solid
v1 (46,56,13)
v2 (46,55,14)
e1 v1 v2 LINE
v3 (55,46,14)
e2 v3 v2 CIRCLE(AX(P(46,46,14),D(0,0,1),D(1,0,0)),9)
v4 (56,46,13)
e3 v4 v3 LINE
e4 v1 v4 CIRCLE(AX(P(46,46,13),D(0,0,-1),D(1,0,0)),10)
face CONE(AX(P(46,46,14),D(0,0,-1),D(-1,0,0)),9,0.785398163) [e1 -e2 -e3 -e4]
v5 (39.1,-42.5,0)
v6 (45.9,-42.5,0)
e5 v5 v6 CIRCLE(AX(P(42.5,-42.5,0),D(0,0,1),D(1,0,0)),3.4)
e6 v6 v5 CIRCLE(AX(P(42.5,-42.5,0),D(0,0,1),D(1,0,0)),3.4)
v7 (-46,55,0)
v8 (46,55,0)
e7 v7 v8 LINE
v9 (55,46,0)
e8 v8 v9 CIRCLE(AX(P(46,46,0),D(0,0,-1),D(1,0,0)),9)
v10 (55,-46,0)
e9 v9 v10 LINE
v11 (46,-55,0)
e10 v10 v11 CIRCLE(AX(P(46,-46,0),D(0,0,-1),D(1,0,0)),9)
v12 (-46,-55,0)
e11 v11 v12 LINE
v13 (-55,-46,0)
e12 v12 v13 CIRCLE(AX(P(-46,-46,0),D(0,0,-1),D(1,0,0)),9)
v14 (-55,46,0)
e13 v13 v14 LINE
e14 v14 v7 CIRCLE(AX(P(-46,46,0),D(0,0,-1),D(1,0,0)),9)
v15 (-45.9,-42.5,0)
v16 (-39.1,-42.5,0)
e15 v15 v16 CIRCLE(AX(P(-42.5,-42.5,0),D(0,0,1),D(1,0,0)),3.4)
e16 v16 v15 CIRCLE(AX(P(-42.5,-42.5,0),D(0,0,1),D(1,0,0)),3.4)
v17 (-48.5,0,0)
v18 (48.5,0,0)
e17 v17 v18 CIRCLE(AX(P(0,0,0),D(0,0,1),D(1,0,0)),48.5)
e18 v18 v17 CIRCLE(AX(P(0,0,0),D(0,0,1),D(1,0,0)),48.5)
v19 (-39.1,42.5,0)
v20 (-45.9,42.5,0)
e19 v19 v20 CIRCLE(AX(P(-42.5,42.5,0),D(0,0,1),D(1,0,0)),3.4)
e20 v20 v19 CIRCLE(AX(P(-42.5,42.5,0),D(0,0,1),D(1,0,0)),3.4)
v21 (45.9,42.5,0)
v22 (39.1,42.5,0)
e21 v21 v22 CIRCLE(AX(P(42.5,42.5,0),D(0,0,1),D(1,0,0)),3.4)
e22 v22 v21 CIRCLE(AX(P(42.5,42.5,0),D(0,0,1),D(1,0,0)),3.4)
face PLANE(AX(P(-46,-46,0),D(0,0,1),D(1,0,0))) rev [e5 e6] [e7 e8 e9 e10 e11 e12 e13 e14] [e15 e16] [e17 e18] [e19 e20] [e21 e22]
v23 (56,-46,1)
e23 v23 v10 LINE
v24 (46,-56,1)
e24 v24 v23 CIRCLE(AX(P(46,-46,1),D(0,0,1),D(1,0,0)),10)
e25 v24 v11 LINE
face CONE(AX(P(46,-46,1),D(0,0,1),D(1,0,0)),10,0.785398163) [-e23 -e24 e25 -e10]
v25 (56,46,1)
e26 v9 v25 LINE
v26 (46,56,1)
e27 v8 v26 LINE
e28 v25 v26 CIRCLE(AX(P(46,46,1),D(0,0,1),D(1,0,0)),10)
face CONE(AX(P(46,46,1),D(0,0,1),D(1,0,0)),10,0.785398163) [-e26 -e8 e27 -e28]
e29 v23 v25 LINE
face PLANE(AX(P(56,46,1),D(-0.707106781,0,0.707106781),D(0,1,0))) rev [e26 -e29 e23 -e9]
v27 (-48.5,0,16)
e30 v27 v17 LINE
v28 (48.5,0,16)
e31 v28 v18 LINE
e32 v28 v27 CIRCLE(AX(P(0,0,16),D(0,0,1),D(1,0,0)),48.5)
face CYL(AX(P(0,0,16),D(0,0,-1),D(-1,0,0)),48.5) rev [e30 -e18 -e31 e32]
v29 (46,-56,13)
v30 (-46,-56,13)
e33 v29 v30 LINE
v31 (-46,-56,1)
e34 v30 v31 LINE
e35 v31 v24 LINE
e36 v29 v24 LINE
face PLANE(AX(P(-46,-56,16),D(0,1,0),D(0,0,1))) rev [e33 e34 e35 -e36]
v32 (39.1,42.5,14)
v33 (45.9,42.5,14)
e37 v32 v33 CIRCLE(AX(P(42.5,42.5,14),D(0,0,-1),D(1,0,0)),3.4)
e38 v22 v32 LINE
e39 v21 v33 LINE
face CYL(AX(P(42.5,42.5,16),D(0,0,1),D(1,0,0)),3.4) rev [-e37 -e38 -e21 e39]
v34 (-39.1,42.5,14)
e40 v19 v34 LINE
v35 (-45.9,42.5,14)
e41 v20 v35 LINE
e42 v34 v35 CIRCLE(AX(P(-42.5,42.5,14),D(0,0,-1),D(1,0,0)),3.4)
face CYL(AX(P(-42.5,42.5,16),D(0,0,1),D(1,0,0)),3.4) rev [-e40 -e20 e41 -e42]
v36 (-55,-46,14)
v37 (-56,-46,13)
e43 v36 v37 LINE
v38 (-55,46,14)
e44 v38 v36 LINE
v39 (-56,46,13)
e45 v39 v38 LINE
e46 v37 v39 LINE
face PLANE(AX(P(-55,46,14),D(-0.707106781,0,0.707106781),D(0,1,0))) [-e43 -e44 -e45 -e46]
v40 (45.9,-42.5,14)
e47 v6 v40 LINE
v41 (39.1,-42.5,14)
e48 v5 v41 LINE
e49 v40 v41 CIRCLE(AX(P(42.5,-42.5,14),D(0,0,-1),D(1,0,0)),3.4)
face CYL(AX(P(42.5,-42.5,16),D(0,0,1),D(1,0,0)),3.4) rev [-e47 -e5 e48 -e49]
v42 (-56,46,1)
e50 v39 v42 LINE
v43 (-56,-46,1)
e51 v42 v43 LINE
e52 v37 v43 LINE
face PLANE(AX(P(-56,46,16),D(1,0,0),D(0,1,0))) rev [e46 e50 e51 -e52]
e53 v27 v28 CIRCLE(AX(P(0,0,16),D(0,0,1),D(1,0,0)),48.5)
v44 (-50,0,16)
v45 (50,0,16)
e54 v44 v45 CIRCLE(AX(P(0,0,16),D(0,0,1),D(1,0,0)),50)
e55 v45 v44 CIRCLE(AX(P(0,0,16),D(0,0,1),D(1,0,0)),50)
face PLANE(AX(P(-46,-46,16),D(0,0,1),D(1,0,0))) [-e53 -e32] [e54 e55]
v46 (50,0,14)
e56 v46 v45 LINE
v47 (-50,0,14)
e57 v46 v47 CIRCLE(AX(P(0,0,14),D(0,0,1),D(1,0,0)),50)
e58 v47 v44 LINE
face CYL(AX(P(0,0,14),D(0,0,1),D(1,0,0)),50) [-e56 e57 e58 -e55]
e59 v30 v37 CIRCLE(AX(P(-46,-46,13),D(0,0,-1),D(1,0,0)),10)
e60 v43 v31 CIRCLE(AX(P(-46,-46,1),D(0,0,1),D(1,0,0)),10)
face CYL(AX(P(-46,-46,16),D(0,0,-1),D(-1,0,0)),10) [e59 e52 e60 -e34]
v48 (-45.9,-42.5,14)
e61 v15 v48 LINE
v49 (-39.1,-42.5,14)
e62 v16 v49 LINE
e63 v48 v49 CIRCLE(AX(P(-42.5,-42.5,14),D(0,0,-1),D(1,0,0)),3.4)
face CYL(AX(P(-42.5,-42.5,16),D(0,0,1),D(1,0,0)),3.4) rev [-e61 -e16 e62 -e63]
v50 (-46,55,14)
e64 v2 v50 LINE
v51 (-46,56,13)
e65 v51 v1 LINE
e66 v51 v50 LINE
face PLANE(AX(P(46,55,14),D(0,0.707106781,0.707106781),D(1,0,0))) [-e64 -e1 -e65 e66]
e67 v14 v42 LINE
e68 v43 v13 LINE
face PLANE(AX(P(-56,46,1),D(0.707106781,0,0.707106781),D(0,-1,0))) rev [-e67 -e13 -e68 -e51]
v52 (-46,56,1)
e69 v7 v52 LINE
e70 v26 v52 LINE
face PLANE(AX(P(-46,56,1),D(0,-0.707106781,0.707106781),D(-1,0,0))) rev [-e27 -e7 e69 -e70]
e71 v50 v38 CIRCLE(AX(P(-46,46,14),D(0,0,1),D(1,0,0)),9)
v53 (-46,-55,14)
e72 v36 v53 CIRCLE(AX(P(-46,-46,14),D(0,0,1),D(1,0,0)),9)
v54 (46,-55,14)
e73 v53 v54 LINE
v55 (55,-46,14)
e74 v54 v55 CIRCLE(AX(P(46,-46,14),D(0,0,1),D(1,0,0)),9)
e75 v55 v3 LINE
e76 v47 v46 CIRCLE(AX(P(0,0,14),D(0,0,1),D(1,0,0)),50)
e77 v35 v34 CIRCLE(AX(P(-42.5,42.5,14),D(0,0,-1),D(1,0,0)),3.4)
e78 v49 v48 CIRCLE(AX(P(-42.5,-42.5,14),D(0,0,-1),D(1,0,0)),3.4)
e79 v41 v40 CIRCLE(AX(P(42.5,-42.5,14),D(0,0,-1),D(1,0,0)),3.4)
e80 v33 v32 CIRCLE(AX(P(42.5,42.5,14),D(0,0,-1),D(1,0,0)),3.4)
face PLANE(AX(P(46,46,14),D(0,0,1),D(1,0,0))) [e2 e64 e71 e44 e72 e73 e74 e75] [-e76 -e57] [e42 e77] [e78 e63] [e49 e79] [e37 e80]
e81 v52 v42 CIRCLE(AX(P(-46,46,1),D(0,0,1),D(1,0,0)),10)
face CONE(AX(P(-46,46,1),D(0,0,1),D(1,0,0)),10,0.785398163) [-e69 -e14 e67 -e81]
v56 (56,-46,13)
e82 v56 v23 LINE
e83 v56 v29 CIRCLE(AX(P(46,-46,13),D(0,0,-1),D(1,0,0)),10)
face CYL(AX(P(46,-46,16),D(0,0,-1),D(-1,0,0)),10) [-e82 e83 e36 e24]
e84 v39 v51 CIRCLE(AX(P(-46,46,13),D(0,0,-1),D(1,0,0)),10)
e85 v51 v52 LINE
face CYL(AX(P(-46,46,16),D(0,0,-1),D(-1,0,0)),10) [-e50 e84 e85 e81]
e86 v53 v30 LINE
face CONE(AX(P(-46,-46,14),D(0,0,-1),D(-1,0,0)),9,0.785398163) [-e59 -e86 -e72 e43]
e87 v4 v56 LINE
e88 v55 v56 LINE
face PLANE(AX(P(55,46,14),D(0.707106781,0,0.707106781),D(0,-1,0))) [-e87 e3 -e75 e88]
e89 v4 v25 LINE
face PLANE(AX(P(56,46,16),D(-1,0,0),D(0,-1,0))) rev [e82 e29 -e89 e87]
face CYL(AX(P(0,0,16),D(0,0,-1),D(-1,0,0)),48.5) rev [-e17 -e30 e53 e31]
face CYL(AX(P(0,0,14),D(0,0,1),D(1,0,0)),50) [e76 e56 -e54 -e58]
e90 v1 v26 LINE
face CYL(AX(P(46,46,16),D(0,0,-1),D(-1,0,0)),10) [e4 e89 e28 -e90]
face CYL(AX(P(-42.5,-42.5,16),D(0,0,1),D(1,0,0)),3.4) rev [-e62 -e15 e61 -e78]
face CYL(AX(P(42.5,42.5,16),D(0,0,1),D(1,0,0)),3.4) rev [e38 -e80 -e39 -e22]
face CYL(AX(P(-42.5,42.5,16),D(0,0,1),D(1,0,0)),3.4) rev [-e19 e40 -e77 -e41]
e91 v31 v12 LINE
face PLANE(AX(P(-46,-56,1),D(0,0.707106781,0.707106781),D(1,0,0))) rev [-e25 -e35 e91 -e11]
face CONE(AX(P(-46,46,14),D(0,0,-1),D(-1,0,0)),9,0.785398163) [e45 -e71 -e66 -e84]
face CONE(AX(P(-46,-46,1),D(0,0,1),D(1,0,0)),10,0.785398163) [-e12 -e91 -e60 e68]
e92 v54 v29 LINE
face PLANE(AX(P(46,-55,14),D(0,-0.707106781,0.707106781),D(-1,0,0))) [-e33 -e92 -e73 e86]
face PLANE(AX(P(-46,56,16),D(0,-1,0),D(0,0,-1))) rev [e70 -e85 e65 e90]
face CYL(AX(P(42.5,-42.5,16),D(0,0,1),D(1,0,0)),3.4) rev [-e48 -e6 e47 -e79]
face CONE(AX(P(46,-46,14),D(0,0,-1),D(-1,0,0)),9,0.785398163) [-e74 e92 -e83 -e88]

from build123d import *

# Parameters (mm, degrees)
SKETCH1_R           = 48.5
BOSS_EXTRUDE1_DEPTH = 16
SKETCH2_R           = 3.35
CUT_EXTRUDE1_DEPTH  = 81.796039507
M8_TAPPED_HOLE2_D   = 6.8
CUT_EXTRUDE2_START  = -2
SKETCH5_R           = 50
CUT_EXTRUDE2_DEPTH  = 2
CHAMFER1_SIZE       = 1


with BuildPart() as part:
    # Sketch1 → Boss-Extrude1 (new body)
    with BuildSketch(Plane.XY):
        with BuildLine():
            Line((-46, 56), (46, 56))
            ThreePointArc((46, 56), (53.071067812, 53.071067812), (56, 46))
            Line((56, 46), (56, -46))
            ThreePointArc((56, -46), (53.071067812, -53.071067812), (46, -56))
            Line((46, -56), (-46, -56))
            ThreePointArc((-46, -56), (-53.071067812, -53.071067812), (-56, -46))
            Line((-56, -46), (-56, 46))
            ThreePointArc((-56, 46), (-53.071067812, 53.071067812), (-46, 56))
        make_face()
        Circle(SKETCH1_R, mode=Mode.SUBTRACT)
    extrude(amount=BOSS_EXTRUDE1_DEPTH)

    # Sketch2 → Cut-Extrude1 (cut, through all)
    with BuildSketch(Plane.XY.offset(16)):
        with Locations((-42.5, 42.5)):
            Circle(SKETCH2_R)
        with Locations((42.5, 42.5)):
            Circle(SKETCH2_R)
        with Locations((42.5, -42.5)):
            Circle(SKETCH2_R)
        with Locations((-42.5, -42.5)):
            Circle(SKETCH2_R)
    extrude(amount=-CUT_EXTRUDE1_DEPTH, mode=Mode.SUBTRACT)

    # M8 Tapped Hole2 (through all)
    with Locations(Plane.XY.offset(16)):
        with Locations((-42.5, 42.5), (42.5, 42.5), (42.5, -42.5), (-42.5, -42.5)):
            Hole(M8_TAPPED_HOLE2_D / 2)

    # Sketch5 → Cut-Extrude2 (cut)
    with BuildSketch(Plane.XY.offset(16).offset(CUT_EXTRUDE2_START)):
        with BuildLine():
            Line((56, -46), (56, 46))
            ThreePointArc((56, 46), (53.071067812, 53.071067812), (46, 56))
            Line((46, 56), (-46, 56))
            ThreePointArc((-46, 56), (-53.071067812, 53.071067812), (-56, 46))
            Line((-56, 46), (-56, -46))
            ThreePointArc((-56, -46), (-53.071067812, -53.071067812), (-46, -56))
            Line((-46, -56), (46, -56))
            ThreePointArc((46, -56), (53.071067812, -53.071067812), (56, -46))
        make_face()
        Circle(SKETCH5_R, mode=Mode.SUBTRACT)
    extrude(amount=CUT_EXTRUDE2_DEPTH, mode=Mode.SUBTRACT)

    # Chamfer1
    chamfer1_edges = [part.edges().sort_by_distance(p)[0] for p in [
        (56, 0, 0),
        (53.071067812, -53.071067812, 0),
        (0, -56, 0),
        (-53.071067812, -53.071067812, 0),
        (-56, 0, 0),
        (-53.071067812, 53.071067812, 0),
        (0, 56, 0),
        (53.071067812, 53.071067812, 14),
        (56, 0, 14),
        (53.071067812, -53.071067812, 14),
        (0, -56, 14),
        (-53.071067812, -53.071067812, 14),
        (-56, 0, 14),
        (-53.071067812, 53.071067812, 14),
        (0, 56, 14),
        (53.071067812, 53.071067812, 0),
    ]]
    chamfer(chamfer1_edges, length=CHAMFER1_SIZE)


solid = part.part
